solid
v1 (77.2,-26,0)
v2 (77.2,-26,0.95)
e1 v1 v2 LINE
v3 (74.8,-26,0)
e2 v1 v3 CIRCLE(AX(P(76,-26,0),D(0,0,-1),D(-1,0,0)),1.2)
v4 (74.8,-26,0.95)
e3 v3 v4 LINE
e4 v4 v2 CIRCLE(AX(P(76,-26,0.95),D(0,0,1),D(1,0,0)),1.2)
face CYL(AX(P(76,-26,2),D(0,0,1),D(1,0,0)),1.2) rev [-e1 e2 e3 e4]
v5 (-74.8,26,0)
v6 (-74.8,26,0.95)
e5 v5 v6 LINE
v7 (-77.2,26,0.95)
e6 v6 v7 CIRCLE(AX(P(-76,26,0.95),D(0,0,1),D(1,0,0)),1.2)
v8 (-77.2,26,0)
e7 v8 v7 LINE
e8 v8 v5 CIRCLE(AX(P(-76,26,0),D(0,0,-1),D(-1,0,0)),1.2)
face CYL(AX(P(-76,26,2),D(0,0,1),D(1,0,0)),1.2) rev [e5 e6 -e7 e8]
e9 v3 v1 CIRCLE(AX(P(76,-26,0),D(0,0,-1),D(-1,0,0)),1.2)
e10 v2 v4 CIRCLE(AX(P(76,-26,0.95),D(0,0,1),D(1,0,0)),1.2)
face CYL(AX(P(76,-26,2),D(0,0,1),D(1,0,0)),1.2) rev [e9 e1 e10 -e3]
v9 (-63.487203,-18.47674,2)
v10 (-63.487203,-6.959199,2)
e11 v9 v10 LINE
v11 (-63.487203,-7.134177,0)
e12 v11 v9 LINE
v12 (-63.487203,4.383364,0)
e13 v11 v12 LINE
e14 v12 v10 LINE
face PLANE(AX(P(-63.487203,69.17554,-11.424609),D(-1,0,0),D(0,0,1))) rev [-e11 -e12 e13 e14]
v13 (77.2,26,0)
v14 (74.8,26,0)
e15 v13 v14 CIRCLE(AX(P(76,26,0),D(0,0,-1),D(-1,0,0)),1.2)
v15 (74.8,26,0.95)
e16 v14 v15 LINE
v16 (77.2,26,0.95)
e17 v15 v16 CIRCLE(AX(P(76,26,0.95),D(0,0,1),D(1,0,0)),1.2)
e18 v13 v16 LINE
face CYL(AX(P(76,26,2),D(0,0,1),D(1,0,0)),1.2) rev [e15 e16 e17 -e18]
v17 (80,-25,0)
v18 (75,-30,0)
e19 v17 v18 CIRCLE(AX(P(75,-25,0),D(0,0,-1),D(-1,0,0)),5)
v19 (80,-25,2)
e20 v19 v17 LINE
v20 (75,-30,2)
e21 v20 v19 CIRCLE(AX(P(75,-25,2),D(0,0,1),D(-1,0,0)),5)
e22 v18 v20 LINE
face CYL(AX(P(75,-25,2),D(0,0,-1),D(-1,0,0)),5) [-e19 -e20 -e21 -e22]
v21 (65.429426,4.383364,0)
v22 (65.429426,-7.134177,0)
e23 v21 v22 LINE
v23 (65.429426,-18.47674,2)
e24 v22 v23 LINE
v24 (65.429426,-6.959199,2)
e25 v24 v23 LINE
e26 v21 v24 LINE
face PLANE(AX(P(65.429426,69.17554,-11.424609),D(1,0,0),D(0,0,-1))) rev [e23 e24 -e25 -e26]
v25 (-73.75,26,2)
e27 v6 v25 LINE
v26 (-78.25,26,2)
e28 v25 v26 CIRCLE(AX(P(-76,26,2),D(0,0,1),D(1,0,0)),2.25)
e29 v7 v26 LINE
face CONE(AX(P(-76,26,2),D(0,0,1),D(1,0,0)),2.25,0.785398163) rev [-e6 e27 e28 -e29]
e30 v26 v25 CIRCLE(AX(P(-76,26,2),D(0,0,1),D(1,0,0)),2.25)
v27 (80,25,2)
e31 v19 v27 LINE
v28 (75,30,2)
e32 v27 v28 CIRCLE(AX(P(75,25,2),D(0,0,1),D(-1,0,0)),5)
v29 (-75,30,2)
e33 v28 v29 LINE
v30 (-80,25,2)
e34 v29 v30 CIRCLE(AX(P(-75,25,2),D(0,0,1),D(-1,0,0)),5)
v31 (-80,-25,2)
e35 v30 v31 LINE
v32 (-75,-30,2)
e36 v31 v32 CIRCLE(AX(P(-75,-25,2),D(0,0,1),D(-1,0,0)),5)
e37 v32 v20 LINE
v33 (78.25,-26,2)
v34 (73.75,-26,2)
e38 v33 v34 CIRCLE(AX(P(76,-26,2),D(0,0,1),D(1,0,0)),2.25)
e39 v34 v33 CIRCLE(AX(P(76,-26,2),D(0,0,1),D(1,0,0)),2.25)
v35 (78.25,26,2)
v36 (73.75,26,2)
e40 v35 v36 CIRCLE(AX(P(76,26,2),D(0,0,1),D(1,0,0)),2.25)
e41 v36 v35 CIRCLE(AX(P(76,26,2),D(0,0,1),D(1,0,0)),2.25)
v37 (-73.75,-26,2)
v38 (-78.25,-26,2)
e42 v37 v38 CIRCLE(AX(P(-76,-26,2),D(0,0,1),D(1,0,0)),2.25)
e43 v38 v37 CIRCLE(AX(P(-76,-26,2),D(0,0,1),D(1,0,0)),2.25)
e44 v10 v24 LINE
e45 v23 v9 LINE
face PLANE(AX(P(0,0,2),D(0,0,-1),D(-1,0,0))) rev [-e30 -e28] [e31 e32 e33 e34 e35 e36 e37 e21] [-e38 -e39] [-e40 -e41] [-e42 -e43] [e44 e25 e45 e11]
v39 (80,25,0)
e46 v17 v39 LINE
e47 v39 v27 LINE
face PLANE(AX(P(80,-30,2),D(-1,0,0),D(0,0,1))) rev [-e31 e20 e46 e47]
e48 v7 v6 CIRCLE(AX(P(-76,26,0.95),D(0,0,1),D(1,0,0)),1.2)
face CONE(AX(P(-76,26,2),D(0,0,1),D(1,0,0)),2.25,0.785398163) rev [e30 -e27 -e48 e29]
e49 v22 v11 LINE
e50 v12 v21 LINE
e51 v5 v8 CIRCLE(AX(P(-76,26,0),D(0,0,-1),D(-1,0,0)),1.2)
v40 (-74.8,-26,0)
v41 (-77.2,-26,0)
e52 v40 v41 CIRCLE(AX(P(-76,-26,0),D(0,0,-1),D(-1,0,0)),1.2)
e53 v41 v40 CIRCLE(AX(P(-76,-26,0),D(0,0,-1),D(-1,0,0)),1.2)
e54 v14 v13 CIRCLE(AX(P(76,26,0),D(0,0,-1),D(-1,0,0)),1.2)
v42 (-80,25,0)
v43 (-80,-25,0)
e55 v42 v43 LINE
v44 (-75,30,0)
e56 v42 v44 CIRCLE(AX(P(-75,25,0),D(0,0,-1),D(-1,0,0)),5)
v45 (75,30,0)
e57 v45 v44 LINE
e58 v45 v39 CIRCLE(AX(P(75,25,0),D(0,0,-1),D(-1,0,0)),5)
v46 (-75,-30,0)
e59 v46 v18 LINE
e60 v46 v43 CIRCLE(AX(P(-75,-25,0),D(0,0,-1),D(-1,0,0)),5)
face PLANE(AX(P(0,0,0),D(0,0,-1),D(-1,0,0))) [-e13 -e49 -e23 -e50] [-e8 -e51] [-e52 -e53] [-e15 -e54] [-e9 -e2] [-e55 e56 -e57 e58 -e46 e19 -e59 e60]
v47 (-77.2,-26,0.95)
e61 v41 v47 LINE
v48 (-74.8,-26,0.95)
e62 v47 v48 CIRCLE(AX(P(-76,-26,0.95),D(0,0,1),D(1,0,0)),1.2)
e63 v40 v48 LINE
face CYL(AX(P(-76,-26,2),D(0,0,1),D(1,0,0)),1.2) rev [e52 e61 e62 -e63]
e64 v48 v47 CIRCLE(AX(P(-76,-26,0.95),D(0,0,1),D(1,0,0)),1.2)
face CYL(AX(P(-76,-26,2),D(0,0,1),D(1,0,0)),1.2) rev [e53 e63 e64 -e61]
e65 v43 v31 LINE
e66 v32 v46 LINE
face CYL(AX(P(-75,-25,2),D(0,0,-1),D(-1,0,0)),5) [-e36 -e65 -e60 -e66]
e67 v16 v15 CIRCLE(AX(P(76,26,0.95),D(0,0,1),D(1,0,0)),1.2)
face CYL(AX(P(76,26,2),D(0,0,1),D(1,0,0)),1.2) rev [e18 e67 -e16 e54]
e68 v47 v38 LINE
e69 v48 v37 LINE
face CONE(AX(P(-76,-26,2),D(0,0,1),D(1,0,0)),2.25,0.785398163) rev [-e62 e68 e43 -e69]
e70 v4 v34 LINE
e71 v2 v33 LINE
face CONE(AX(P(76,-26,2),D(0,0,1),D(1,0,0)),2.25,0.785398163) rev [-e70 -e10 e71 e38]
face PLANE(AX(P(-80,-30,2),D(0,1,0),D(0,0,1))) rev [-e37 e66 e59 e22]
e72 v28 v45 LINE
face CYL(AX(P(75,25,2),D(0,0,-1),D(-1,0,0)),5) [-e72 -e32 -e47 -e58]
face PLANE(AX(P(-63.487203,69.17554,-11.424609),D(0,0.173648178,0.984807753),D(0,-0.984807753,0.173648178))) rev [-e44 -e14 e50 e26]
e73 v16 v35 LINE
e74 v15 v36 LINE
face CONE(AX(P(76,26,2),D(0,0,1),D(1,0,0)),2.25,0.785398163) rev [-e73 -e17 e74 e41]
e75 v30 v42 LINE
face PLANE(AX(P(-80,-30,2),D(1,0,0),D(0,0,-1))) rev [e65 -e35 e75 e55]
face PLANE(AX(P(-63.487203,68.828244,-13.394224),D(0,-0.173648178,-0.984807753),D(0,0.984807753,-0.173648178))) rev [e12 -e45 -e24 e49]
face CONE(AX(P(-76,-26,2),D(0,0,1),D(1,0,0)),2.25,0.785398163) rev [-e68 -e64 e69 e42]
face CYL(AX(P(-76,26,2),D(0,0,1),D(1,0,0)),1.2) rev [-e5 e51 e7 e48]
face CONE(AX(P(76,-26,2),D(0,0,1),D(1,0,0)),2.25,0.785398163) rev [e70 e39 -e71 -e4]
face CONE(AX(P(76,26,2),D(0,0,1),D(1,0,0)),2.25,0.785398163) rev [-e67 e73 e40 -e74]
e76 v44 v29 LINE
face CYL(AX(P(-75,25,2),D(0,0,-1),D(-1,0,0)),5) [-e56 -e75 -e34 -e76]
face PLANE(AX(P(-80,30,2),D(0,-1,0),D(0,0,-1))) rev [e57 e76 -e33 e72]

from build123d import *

# Parameters (mm, degrees)
SKETCH1_W                                         = 160
SKETCH1_H                                         = 60
BOSS_EXTRUDE1_DEPTH                               = 2
SKETCH2_R                                         = 0.5
CUT_EXTRUDE1_DEPTH                                = 2
PILOT_HOLE_SIZE_PER_CROSS_SLOTTED_COU_D           = 2.4
PILOT_HOLE_SIZE_PER_CROSS_SLOTTED_COU_DEPTH       = 7.5
PILOT_HOLE_SIZE_PER_CROSS_SLOTTED_COU_CSINK_D     = 4.5
PILOT_HOLE_SIZE_PER_CROSS_SLOTTED_COU_CSINK_ANGLE = 90
PILOT_HOLE_SIZE_PER_CROSS_SLOTTED_COU_TIP         = 0.721032743
SKETCH6_W                                         = 128.916628893
SKETCH6_H                                         = 2
CUT_EXTRUDE3_DEPTH                                = 100
FILLET1_R                                         = 5


with BuildPart() as part:
    # Sketch1 → Boss-Extrude1 (new body)
    with BuildSketch(Plane.XY):
        Rectangle(SKETCH1_W, SKETCH1_H)
    extrude(amount=BOSS_EXTRUDE1_DEPTH)

    # Sketch2 → Cut-Extrude1 (cut)
    with BuildSketch(Plane.XY.offset(2)):
        with Locations((-76, 26)):
            Circle(SKETCH2_R)
        with Locations(Location((76, 26, 0), (0, 0, 180))):
            Circle(SKETCH2_R)
        with Locations((76, -26)):
            Circle(SKETCH2_R)
        with Locations(Location((-76, -26, 0), (0, 0, 180))):
            Circle(SKETCH2_R)
    extrude(amount=-CUT_EXTRUDE1_DEPTH, mode=Mode.SUBTRACT)

    # Pilot hole size (% per cross) slotted countersunk wood screw type1
    with Locations(Plane.XY.offset(2)):
        with Locations((-76, 26), (76, 26), (76, -26), (-76, -26)):
            CounterSinkHole(PILOT_HOLE_SIZE_PER_CROSS_SLOTTED_COU_D / 2, PILOT_HOLE_SIZE_PER_CROSS_SLOTTED_COU_CSINK_D / 2, depth=PILOT_HOLE_SIZE_PER_CROSS_SLOTTED_COU_DEPTH, counter_sink_angle=PILOT_HOLE_SIZE_PER_CROSS_SLOTTED_COU_CSINK_ANGLE)
            with Locations((0, 0, -(PILOT_HOLE_SIZE_PER_CROSS_SLOTTED_COU_DEPTH + PILOT_HOLE_SIZE_PER_CROSS_SLOTTED_COU_TIP / 2))):  # 118° drill point
                Cone(0, PILOT_HOLE_SIZE_PER_CROSS_SLOTTED_COU_D / 2, PILOT_HOLE_SIZE_PER_CROSS_SLOTTED_COU_TIP, mode=Mode.SUBTRACT)

    # Sketch6 → Cut-Extrude3 (cut)
    with BuildSketch(Plane(origin=(0, -29.437409455, 5.190609529), x_dir=(1, 0, 0), z_dir=(0, -0.9848077530122086, 0.17364817766692736))):
        with Locations((0.971111813, -0.2388368)):
            Rectangle(SKETCH6_W, SKETCH6_H)
    extrude(amount=-CUT_EXTRUDE3_DEPTH, mode=Mode.SUBTRACT)

    # Fillet1
    fillet1_edges = [part.edges().sort_by_distance(p)[0] for p in [
        (80, -30, 1),
        (-80, -30, 1),
        (-80, 30, 1),
        (80, 30, 1),
    ]]
    fillet(fillet1_edges, radius=FILLET1_R)


solid = part.part
